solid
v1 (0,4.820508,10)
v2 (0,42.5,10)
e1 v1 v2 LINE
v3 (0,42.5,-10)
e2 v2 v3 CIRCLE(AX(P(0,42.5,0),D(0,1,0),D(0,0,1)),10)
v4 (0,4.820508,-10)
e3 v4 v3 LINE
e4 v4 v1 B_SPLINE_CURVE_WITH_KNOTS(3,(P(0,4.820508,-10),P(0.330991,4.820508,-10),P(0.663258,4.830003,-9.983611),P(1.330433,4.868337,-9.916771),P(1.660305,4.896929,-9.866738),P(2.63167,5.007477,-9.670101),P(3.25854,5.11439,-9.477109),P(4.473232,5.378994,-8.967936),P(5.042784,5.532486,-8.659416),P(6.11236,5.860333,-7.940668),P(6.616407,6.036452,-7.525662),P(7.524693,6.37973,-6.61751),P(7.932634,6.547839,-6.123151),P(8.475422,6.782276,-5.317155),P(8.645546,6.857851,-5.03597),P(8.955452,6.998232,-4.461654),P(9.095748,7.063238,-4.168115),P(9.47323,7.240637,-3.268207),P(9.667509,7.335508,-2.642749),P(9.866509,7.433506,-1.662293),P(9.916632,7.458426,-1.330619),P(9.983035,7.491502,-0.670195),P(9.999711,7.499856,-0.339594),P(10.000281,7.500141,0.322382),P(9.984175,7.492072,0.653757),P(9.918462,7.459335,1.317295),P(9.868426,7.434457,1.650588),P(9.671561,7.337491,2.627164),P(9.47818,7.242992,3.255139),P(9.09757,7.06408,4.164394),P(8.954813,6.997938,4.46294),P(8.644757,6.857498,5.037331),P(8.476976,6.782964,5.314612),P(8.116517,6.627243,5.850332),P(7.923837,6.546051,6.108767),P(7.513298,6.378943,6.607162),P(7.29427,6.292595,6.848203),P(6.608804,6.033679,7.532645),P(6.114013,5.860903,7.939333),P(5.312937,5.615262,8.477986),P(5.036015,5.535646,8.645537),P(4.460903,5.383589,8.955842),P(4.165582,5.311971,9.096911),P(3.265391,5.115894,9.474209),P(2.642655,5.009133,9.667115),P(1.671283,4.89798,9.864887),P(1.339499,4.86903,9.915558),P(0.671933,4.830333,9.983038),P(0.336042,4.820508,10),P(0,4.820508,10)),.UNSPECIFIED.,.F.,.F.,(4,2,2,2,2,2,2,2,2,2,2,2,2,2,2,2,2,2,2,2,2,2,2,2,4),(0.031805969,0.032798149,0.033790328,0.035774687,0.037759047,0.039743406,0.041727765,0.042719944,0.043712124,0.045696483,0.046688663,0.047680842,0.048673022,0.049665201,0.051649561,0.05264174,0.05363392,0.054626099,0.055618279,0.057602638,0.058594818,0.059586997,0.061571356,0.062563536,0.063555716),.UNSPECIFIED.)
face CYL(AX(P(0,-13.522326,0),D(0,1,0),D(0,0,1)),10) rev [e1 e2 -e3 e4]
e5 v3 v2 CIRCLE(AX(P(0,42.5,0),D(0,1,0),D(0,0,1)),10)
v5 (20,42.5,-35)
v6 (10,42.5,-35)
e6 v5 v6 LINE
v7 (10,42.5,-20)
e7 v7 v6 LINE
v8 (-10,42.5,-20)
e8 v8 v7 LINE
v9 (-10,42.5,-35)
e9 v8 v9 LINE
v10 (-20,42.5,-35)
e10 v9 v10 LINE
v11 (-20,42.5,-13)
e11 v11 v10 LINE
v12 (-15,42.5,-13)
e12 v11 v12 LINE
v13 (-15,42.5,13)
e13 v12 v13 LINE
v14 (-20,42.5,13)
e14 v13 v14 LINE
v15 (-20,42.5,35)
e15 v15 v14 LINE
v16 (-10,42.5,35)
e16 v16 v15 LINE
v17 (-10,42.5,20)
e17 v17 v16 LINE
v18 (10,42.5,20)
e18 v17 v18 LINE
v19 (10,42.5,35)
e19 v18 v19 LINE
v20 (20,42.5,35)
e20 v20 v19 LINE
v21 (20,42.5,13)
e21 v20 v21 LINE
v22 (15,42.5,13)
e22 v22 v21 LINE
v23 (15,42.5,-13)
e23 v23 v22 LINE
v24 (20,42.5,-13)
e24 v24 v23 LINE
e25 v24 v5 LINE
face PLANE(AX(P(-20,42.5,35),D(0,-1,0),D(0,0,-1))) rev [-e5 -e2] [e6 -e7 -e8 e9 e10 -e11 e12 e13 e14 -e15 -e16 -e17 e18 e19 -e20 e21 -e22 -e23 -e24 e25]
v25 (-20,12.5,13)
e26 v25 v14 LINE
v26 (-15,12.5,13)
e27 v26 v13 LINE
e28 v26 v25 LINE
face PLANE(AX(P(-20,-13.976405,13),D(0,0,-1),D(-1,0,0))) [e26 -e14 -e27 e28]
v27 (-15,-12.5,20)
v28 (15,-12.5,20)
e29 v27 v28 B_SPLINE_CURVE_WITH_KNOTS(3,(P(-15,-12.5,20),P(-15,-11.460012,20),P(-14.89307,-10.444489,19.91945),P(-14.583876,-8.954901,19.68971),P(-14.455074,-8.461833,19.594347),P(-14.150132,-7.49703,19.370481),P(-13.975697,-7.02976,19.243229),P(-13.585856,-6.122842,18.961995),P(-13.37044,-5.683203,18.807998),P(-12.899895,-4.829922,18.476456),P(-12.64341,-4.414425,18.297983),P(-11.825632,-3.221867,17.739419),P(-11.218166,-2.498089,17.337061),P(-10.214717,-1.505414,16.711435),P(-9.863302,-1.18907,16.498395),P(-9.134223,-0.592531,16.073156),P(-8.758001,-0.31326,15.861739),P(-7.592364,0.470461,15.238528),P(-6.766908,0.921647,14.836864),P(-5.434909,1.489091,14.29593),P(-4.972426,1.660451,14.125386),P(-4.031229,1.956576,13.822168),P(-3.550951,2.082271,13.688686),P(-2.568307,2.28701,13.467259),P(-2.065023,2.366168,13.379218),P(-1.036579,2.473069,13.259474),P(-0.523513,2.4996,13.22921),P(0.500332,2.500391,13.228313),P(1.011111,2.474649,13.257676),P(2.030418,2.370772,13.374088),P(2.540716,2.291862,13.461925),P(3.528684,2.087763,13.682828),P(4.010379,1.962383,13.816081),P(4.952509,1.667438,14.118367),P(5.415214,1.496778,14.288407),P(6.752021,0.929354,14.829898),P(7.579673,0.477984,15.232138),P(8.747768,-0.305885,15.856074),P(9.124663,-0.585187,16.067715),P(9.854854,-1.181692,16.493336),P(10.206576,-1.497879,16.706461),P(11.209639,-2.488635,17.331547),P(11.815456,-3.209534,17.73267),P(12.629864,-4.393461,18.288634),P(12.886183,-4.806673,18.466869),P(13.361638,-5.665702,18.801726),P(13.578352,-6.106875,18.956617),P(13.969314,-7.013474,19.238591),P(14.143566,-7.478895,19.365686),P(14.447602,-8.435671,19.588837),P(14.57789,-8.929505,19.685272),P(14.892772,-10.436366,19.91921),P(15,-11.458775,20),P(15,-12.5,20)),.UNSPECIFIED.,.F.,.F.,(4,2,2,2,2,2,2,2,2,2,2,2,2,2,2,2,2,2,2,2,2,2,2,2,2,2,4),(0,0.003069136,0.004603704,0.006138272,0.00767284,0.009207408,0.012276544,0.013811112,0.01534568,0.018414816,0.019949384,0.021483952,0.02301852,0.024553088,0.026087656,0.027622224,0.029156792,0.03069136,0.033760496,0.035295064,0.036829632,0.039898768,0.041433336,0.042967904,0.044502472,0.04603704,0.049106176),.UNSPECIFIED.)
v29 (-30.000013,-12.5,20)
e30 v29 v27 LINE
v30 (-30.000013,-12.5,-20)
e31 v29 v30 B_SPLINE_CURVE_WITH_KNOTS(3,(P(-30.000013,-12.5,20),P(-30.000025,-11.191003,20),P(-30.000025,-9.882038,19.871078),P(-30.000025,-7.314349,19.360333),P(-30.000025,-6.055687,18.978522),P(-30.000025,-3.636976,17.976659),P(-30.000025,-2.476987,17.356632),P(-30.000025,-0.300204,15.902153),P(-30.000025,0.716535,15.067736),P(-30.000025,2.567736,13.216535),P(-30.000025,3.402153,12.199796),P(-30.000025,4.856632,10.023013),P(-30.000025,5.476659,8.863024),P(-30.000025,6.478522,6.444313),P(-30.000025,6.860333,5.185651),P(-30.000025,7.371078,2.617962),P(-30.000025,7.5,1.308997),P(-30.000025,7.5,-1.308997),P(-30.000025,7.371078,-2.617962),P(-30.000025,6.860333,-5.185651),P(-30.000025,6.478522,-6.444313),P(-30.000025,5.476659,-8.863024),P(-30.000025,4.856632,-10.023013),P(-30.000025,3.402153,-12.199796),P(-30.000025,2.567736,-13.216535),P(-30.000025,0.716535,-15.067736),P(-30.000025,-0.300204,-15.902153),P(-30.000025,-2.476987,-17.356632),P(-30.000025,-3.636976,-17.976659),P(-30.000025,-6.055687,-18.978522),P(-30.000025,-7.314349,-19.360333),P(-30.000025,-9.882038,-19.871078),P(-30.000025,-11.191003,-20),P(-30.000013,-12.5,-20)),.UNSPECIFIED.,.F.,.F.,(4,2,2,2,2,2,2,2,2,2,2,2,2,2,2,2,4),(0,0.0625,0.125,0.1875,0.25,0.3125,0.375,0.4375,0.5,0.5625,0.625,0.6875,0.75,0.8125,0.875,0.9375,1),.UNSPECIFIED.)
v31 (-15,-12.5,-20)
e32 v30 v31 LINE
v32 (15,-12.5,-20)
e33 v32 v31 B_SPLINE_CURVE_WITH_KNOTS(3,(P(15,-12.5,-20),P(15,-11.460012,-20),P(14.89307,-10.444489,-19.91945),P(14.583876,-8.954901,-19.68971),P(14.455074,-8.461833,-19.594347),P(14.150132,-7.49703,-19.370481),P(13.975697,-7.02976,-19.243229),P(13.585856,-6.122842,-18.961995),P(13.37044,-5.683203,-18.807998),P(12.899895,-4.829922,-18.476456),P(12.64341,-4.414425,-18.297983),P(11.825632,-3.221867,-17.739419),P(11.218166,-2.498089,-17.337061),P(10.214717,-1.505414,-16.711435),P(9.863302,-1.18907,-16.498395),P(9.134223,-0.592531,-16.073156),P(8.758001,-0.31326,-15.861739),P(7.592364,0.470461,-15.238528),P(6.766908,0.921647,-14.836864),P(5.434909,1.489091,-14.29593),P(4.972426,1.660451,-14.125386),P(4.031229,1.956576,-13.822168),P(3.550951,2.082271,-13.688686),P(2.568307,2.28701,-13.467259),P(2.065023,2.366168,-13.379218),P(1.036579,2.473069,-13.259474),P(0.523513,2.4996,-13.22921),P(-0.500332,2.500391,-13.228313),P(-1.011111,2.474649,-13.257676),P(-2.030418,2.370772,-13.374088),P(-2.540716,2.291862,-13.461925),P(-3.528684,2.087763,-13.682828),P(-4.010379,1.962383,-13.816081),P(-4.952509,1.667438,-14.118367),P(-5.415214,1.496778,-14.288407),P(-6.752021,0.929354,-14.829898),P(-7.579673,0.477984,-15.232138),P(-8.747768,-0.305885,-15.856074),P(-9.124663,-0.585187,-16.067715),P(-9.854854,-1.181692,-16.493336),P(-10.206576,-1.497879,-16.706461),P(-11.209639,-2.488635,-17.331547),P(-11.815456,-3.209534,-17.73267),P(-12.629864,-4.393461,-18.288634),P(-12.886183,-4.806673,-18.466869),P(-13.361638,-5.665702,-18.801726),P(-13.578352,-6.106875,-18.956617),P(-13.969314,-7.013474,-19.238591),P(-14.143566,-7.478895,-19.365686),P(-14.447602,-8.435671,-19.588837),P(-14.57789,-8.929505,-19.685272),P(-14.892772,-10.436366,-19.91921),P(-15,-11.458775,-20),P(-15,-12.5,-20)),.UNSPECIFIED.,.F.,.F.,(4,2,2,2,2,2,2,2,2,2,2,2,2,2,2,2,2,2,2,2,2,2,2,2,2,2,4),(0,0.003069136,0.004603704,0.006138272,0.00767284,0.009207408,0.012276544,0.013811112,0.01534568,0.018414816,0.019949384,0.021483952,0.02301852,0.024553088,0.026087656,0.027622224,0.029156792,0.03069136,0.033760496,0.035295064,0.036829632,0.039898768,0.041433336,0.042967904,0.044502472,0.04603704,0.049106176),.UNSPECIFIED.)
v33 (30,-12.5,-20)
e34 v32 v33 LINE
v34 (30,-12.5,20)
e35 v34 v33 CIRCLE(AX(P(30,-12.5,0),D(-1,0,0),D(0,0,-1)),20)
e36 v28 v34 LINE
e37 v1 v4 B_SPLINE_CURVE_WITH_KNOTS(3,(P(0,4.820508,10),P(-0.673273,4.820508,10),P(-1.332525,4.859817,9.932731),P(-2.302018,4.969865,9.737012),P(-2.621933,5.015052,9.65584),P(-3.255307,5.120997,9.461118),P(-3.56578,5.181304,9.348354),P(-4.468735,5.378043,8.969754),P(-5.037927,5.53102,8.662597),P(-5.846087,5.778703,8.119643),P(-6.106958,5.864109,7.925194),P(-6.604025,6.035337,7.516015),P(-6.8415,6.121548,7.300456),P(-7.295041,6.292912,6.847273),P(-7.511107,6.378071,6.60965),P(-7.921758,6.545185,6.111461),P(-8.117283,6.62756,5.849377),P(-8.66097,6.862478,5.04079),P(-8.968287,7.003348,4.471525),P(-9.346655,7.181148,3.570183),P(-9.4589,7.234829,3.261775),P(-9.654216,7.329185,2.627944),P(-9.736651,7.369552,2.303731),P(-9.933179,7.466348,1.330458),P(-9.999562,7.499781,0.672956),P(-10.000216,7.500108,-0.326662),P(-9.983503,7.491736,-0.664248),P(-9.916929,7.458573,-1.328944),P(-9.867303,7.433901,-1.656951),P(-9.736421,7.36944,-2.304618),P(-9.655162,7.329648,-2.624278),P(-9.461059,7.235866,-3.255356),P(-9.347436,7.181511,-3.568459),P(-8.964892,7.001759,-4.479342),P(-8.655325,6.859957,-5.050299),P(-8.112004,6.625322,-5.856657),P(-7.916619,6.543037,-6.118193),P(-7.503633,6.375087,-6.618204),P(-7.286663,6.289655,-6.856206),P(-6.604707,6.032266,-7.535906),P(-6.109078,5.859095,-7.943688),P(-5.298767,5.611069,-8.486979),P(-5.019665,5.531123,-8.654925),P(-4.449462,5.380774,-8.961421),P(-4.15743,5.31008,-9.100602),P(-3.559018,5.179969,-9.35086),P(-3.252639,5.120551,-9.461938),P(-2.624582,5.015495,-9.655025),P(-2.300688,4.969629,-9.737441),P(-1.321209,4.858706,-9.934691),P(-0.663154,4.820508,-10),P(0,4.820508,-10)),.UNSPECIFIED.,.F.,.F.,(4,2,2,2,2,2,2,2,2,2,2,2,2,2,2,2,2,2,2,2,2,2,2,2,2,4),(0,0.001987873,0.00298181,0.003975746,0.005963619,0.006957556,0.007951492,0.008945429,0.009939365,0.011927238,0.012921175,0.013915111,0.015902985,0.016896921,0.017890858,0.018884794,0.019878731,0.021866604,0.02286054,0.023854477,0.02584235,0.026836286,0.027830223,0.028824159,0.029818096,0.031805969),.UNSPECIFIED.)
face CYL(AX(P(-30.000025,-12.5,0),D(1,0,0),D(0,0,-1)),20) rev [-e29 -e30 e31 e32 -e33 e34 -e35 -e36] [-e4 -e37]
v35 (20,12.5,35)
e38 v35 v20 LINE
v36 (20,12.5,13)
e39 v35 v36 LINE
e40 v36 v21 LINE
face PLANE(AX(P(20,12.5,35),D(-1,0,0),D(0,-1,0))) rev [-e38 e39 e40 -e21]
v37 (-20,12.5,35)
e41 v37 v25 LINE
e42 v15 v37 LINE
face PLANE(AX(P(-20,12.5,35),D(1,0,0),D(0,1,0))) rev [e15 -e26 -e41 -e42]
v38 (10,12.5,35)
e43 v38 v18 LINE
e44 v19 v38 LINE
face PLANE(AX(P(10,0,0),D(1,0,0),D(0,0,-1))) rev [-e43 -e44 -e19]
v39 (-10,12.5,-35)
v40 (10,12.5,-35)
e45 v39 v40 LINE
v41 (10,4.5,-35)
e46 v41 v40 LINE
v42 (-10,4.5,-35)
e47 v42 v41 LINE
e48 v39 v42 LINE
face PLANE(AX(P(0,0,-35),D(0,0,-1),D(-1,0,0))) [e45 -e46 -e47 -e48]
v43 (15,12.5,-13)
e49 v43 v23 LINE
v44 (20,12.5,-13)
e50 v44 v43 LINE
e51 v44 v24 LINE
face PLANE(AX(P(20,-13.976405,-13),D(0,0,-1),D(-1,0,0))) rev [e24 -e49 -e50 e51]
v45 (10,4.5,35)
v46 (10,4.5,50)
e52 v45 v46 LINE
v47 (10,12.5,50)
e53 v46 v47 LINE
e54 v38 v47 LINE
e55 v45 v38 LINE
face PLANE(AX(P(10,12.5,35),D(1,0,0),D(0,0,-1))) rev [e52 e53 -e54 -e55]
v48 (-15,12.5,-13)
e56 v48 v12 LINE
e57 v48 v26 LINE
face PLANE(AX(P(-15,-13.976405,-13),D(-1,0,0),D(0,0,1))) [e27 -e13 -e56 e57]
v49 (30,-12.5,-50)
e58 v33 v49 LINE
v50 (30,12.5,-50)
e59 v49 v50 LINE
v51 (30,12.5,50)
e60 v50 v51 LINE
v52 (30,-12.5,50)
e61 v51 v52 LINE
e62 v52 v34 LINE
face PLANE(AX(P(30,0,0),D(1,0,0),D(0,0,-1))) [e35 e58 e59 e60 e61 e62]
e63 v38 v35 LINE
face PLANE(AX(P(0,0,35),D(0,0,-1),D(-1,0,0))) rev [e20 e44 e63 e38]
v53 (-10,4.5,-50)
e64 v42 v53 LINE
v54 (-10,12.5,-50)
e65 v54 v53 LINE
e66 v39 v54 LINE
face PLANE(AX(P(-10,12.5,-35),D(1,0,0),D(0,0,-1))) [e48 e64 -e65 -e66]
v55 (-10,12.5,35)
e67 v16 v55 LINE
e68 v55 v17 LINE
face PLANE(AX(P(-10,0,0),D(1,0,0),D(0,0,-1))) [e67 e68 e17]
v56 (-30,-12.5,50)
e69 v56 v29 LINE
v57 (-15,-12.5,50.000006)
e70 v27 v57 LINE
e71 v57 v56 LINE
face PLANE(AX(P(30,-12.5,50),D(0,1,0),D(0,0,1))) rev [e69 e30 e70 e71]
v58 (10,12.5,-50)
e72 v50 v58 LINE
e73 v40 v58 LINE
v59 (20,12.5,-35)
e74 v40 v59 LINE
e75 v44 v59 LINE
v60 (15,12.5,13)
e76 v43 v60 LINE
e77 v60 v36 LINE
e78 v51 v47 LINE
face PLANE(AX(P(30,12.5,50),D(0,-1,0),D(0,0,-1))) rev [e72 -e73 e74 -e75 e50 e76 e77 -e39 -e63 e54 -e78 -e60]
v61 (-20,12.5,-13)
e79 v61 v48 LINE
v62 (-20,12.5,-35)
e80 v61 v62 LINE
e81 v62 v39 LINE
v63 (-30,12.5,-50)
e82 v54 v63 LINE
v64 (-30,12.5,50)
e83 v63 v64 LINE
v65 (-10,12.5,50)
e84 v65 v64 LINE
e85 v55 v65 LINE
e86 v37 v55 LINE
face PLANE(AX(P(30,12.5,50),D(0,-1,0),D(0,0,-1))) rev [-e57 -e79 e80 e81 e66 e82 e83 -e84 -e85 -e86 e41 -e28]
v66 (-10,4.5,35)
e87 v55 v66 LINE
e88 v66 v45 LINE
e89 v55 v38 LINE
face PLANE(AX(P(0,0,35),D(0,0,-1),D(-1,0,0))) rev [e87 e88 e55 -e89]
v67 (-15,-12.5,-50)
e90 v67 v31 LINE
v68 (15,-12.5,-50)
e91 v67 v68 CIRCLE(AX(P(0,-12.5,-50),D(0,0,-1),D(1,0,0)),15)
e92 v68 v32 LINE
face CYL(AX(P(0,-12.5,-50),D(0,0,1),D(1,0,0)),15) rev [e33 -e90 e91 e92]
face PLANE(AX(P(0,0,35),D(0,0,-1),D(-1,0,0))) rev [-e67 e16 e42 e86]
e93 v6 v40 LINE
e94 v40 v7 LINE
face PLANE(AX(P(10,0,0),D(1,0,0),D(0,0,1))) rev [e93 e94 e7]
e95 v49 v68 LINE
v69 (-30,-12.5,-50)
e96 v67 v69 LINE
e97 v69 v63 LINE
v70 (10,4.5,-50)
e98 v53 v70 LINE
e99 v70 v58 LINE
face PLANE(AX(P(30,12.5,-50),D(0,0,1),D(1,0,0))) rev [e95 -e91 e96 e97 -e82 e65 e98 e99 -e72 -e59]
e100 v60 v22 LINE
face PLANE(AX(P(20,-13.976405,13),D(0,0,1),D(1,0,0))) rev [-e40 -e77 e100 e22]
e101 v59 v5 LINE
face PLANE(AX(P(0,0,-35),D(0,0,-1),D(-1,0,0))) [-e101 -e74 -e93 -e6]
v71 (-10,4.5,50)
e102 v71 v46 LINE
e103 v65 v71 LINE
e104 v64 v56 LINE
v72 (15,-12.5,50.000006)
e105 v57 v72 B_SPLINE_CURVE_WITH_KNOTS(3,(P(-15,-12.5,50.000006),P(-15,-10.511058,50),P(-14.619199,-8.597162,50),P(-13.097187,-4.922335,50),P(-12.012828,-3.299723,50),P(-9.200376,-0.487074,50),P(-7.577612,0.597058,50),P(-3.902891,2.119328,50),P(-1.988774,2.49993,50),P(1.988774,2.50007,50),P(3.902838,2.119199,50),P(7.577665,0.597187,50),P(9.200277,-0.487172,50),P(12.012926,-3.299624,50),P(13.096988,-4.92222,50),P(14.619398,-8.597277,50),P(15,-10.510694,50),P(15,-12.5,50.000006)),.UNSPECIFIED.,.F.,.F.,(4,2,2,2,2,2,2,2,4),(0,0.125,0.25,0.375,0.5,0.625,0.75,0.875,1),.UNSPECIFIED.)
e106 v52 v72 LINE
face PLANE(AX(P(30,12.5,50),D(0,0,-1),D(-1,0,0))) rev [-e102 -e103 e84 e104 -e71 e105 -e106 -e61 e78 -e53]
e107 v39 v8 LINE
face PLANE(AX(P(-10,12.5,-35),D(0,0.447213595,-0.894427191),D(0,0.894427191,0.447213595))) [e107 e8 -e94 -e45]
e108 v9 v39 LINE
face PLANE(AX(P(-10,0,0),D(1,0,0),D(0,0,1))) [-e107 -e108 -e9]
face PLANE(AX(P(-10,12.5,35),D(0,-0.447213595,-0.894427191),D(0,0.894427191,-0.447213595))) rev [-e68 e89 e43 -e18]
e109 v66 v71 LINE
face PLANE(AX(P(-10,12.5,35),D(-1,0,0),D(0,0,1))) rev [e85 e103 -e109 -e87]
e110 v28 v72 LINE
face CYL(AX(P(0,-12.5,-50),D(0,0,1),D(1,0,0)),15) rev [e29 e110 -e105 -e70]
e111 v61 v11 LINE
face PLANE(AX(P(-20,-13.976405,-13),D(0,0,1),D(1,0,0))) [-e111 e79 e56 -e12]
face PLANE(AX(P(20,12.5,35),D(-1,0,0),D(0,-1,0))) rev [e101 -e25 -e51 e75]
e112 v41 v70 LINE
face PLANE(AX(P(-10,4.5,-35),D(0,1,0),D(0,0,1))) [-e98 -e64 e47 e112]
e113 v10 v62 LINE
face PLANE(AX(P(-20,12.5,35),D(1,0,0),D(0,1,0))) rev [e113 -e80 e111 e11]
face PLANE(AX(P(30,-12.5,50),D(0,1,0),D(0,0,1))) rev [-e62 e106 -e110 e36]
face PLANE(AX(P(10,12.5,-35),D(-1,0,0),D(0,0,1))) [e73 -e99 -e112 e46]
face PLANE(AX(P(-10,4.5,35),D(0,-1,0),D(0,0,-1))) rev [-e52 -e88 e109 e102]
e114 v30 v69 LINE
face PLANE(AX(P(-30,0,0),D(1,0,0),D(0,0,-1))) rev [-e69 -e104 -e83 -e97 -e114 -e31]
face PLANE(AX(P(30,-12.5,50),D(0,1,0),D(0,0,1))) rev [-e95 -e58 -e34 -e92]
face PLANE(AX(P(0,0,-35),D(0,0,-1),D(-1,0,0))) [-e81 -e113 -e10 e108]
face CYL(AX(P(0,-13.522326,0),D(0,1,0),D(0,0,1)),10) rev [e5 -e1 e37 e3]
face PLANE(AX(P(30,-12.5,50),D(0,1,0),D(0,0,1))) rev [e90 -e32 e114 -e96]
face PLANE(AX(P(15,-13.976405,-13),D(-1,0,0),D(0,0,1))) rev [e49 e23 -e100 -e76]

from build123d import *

# Parameters (mm, degrees)
BASE_BLOCK_PROFILE_W        = 100
BASE_BLOCK_PROFILE_H        = 25
BASE_BLOCK_DEPTH            = 30
END_ARCH_CUT_DEPTH          = 106.148704224
END_ARCH_CUT_DEPTH_BACK     = 106.148704224
CENTER_ARCH_CUT_DEPTH       = 80.096460098
UPPER_BLOCK_PROFILE_W       = 40
UPPER_BLOCK_PROFILE_H       = 30
UPPER_BLOCK_DEPTH           = 35
SIDE_SLOT_PROFILE_W         = 5
SIDE_SLOT_PROFILE_H         = 26
SIDE_SLOT_DEPTH             = 30
TOP_BORE_PROFILE_R          = 10
TOP_BORE_20_DEPTH           = 81.156097878
BASE_NOTCH_PROFILE_W        = 20
BASE_NOTCH_PROFILE_H        = 8
BASE_NOTCH_DEPTH            = 15
TRIANGULAR_RELIEF_CUT_DEPTH = 10


with BuildPart() as part:
    # Base Block Profile → Base Block (new, symmetric)
    with BuildSketch(Plane(origin=(0, 0, 0), x_dir=(0, 0, -1), z_dir=(1, 0, 0))):
        Rectangle(BASE_BLOCK_PROFILE_W, BASE_BLOCK_PROFILE_H)
    extrude(amount=BASE_BLOCK_DEPTH, both=True)

    # End Arch Profile → End Arch Cut (cut, two sides: drawn at the far end of the back side and taken through both)
    with BuildSketch(Plane.XY.offset(50).offset(-END_ARCH_CUT_DEPTH_BACK)):
        with BuildLine():
            ThreePointArc((15, -12.5), (0, 2.5), (-15, -12.5))
            Line((-15, -12.5), (15, -12.5))
        make_face()
    extrude(amount=END_ARCH_CUT_DEPTH + END_ARCH_CUT_DEPTH_BACK, mode=Mode.SUBTRACT)

    # Center Arch Profile → Center Arch Cut (cut, through all)
    with BuildSketch(Plane(origin=(30, 0, 0), x_dir=(0, 0, -1), z_dir=(1, 0, 0))):
        with BuildLine():
            ThreePointArc((20, -12.5), (0, 7.5), (-20, -12.5))
            Line((-20, -12.5), (20, -12.5))
        make_face()
    extrude(amount=-CENTER_ARCH_CUT_DEPTH, mode=Mode.SUBTRACT)

    # Upper Block Profile → Upper Block (add, symmetric)
    with BuildSketch(Plane.XY):
        with Locations((0, 27.5)):
            Rectangle(UPPER_BLOCK_PROFILE_W, UPPER_BLOCK_PROFILE_H)
    extrude(amount=UPPER_BLOCK_DEPTH, both=True)

    # Side Slot Profile → Side Slot (cut)
    with BuildSketch(Plane(origin=(0, 42.5, 0), x_dir=(1, 0, 0), z_dir=(0, 1, 0))):
        with Locations((17.5, 0)):
            Rectangle(SIDE_SLOT_PROFILE_W, SIDE_SLOT_PROFILE_H)
    side_slot = extrude(amount=-SIDE_SLOT_DEPTH, mode=Mode.SUBTRACT)

    # Side Slot Mirror: Side Slot across plane
    add(side_slot.mirror(Plane(origin=(0, 0, 0), x_dir=(0, 0, 1), z_dir=(1, 0, 0))), mode=Mode.SUBTRACT)

    # Top Bore Profile → Top Bore Ø20 (cut, through all)
    with BuildSketch(Plane(origin=(0, 42.5, 0), x_dir=(1, 0, 0), z_dir=(0, 1, 0))):
        with Locations(Location((0, 0, 0), (0, 0, 270))):
            Circle(TOP_BORE_PROFILE_R)
    extrude(amount=-TOP_BORE_20_DEPTH, mode=Mode.SUBTRACT)

    # Base Notch Profile → Base Notch (cut)
    with BuildSketch(Plane.XY.offset(50)):
        with Locations((0, 8.5)):
            Rectangle(BASE_NOTCH_PROFILE_W, BASE_NOTCH_PROFILE_H)
    base_notch = extrude(amount=-BASE_NOTCH_DEPTH, mode=Mode.SUBTRACT)

    # Triangular Relief Profile → Triangular Relief Cut (cut, symmetric)
    with BuildSketch(Plane(origin=(0, 0, 0), x_dir=(0, 0, -1), z_dir=(1, 0, 0))):
        Polygon((-35, 12.5), (-20, 42.5), (-35, 42.5), align=None)
    triangular_relief_cut = extrude(amount=TRIANGULAR_RELIEF_CUT_DEPTH, both=True, mode=Mode.SUBTRACT)

    # Notch and Relief Mirror: Base Notch, Triangular Relief Cut across plane
    add(base_notch.mirror(Plane.XY), mode=Mode.SUBTRACT)
    add(triangular_relief_cut.mirror(Plane.XY), mode=Mode.SUBTRACT)


solid = part.part
